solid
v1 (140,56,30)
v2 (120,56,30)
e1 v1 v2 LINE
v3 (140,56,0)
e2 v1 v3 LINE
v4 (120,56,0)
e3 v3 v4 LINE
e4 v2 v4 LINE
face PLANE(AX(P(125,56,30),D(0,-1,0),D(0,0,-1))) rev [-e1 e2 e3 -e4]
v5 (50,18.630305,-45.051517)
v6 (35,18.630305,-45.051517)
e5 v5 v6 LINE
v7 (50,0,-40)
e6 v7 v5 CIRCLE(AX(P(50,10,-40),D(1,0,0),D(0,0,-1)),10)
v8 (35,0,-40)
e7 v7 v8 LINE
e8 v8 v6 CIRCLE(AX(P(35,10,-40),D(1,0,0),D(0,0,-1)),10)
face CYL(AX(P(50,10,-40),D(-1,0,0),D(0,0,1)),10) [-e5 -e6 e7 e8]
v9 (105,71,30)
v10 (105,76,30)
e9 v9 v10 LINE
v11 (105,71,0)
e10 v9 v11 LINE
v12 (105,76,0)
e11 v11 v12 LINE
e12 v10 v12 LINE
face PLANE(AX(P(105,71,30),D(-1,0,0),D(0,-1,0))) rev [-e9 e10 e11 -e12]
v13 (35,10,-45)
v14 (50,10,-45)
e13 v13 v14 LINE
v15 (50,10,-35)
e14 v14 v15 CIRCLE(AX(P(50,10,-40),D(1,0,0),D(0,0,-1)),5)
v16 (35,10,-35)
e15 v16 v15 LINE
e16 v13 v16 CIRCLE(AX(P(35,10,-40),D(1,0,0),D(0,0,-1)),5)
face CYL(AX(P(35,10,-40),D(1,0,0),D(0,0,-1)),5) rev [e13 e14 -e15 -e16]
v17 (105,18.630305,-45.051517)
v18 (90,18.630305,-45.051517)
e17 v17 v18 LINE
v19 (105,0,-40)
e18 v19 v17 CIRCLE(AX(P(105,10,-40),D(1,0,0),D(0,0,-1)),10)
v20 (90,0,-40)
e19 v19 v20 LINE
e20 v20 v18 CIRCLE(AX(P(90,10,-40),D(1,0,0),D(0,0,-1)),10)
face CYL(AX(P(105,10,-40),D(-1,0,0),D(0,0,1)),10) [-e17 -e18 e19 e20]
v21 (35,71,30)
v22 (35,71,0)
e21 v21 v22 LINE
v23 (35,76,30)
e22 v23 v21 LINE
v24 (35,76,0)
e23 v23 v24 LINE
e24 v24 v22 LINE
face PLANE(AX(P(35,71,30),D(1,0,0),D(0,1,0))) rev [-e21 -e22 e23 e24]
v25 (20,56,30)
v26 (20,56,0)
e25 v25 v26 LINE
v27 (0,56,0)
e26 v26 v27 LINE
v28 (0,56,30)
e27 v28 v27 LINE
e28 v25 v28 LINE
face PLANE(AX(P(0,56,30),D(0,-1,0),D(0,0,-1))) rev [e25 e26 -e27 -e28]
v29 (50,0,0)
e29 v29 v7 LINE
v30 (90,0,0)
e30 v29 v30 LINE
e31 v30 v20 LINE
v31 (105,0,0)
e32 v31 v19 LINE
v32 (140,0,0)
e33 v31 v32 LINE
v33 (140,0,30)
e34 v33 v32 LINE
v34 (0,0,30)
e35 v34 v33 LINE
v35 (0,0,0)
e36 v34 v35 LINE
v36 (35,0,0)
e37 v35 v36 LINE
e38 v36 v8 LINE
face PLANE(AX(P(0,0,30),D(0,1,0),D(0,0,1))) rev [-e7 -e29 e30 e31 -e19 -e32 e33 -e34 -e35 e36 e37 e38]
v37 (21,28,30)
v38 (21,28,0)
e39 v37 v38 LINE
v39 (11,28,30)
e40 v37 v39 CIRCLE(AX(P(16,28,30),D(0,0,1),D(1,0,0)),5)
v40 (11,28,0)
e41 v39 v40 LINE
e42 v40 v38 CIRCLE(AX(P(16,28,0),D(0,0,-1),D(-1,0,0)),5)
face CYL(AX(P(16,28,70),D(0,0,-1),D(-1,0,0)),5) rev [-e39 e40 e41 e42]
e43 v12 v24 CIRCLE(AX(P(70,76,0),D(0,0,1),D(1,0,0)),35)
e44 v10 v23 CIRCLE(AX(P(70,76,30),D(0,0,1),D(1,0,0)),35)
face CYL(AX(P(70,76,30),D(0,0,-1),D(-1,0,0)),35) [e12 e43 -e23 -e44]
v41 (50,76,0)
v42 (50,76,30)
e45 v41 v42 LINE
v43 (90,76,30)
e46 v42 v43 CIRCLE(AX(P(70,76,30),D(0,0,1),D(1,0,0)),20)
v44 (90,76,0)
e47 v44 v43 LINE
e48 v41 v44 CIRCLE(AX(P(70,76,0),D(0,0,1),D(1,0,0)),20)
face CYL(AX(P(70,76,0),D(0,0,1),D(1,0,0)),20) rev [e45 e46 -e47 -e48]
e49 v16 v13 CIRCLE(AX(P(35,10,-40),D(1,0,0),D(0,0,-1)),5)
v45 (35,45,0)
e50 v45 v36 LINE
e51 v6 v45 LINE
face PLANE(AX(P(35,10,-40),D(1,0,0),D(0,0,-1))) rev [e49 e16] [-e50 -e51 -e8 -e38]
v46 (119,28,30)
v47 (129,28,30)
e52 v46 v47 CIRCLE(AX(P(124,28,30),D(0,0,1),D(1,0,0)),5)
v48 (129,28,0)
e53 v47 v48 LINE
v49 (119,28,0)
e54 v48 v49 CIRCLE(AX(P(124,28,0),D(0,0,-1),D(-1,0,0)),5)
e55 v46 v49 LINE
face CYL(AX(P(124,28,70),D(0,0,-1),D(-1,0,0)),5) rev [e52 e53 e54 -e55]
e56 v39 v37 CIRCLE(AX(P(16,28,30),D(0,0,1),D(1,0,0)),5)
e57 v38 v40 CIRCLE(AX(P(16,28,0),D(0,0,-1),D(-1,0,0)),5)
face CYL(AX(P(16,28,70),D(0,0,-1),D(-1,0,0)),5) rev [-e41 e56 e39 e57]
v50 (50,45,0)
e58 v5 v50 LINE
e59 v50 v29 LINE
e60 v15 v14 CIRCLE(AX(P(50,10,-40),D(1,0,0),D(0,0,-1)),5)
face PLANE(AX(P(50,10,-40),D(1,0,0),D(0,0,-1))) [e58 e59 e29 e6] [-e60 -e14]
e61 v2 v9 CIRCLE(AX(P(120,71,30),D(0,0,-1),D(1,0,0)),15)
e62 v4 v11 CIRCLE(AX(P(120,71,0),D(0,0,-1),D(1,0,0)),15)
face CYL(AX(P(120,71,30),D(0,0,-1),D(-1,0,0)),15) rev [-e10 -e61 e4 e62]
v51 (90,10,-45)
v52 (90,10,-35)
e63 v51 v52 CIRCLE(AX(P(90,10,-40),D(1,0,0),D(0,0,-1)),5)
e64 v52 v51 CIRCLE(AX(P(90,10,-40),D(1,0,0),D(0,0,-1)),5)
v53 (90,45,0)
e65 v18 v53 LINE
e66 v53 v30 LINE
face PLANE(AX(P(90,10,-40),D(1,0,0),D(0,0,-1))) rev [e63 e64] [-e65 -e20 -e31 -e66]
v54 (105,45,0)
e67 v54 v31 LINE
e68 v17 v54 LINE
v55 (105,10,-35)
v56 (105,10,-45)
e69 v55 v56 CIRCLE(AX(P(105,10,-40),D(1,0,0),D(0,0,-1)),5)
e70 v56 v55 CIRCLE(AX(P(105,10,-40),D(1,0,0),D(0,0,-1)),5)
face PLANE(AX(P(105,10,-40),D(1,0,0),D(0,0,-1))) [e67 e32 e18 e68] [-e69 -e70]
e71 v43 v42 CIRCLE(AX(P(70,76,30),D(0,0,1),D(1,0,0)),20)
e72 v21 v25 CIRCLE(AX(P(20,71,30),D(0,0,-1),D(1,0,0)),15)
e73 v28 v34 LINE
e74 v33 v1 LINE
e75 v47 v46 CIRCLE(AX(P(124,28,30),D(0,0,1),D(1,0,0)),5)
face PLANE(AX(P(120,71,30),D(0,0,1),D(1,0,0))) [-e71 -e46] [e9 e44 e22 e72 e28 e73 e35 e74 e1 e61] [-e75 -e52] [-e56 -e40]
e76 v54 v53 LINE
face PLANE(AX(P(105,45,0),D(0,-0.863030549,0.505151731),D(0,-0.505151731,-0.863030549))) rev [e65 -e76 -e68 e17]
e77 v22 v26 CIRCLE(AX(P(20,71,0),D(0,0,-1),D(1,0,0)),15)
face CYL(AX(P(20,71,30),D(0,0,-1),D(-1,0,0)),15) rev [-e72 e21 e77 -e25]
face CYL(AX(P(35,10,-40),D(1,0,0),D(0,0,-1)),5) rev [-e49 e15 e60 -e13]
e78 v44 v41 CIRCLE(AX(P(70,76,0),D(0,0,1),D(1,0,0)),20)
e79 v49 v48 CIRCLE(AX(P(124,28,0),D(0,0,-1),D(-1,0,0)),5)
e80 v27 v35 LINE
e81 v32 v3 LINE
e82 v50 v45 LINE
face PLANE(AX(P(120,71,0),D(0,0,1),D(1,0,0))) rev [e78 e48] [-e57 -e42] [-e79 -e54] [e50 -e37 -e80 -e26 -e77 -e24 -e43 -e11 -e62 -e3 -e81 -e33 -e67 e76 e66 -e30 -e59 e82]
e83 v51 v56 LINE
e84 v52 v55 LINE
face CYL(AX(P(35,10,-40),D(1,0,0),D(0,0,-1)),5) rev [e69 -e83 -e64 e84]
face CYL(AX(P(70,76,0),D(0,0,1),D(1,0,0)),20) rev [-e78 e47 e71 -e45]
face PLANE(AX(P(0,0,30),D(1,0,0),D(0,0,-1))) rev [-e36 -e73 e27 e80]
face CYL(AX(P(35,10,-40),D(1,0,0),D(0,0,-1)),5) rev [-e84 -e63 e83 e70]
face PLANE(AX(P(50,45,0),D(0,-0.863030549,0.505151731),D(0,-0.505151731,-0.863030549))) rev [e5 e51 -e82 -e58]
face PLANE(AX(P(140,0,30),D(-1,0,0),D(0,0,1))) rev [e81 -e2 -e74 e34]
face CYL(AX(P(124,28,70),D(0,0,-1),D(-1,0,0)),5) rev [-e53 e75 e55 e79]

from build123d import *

# Parameters (mm, degrees)
BASE_PLATE_DEPTH         = 30
PIVOT_BORE_PROFILE_R     = 20
PIVOT_BORE_DEPTH         = 30
SUPPORT_ARM_DEPTH        = 15
PIVOT_LUG_DEPTH          = 15
LUG_HOLE_PROFILE_R       = 5
LUG_HOLE_DEPTH           = 70
MOUNTING_HOLES_PROFILE_R = 5
MOUNTING_HOLES_2X_DEPTH  = 70


with BuildPart() as part:
    # Base Plate Profile → Base Plate (new body)
    with BuildSketch(Plane.XY):
        with BuildLine():
            Line((0, 0), (0, 56))
            Line((0, 56), (20, 56))
            ThreePointArc((20, 56), (30.606601718, 60.393398282), (35, 71))
            Line((35, 71), (35, 76))
            ThreePointArc((35, 76), (70, 111), (105, 76))
            Line((105, 76), (105, 71))
            ThreePointArc((105, 71), (109.393398282, 60.393398282), (120, 56))
            Line((120, 56), (125, 56))
            Line((125, 56), (140, 56))
            Line((140, 56), (140, 0))
            Line((140, 0), (0, 0))
        make_face()
    extrude(amount=BASE_PLATE_DEPTH)

    # Pivot Bore Profile → Pivot Bore (cut)
    with BuildSketch(Plane.XY.offset(30)):
        with Locations((70, 76)):
            Circle(PIVOT_BORE_PROFILE_R)
    extrude(amount=-PIVOT_BORE_DEPTH, mode=Mode.SUBTRACT)

    # Support Arm Profile → Support Arm (add)
    with BuildSketch(Plane(origin=(35, 0, 0), x_dir=(0, 0, -1), z_dir=(1, 0, 0))):
        with BuildLine():
            Line((0, 0), (0, 45))
            Line((0, 45), (45.051517306, 18.630305493))
            ThreePointArc((45.051517306, 18.630305493), (49.651503897, 7.383041358), (40, 0))
            Line((40, 0), (0, 0))
        make_face()
    extrude(amount=SUPPORT_ARM_DEPTH)

    # Pivot Lug Profile → Pivot Lug (add)
    with BuildSketch(Plane(origin=(90, 0, 0), x_dir=(0, 0, -1), z_dir=(1, 0, 0))):
        with BuildLine():
            Line((0, 0), (0, 45))
            Line((0, 45), (45.051517306, 18.630305493))
            ThreePointArc((45.051517306, 18.630305493), (49.651503897, 7.383041358), (40, 0))
            Line((40, 0), (0, 0))
        make_face()
    extrude(amount=PIVOT_LUG_DEPTH)

    # Lug Hole Profile → Lug Hole (cut)
    with BuildSketch(Plane(origin=(105, 0, 0), x_dir=(0, 0, -1), z_dir=(1, 0, 0))):
        with Locations((40, 10)):
            Circle(LUG_HOLE_PROFILE_R)
    extrude(amount=-LUG_HOLE_DEPTH, mode=Mode.SUBTRACT)

    # Mounting Holes Profile → Mounting Holes 2x (cut)
    with BuildSketch(Plane(origin=(0, 0, 0), x_dir=(-1, 0, 0), z_dir=(0, 0, -1))):
        with Locations((-124, 28)):
            Circle(MOUNTING_HOLES_PROFILE_R)
        with Locations((-16, 28)):
            Circle(MOUNTING_HOLES_PROFILE_R)
    extrude(amount=-MOUNTING_HOLES_2X_DEPTH, mode=Mode.SUBTRACT)


solid = part.part
